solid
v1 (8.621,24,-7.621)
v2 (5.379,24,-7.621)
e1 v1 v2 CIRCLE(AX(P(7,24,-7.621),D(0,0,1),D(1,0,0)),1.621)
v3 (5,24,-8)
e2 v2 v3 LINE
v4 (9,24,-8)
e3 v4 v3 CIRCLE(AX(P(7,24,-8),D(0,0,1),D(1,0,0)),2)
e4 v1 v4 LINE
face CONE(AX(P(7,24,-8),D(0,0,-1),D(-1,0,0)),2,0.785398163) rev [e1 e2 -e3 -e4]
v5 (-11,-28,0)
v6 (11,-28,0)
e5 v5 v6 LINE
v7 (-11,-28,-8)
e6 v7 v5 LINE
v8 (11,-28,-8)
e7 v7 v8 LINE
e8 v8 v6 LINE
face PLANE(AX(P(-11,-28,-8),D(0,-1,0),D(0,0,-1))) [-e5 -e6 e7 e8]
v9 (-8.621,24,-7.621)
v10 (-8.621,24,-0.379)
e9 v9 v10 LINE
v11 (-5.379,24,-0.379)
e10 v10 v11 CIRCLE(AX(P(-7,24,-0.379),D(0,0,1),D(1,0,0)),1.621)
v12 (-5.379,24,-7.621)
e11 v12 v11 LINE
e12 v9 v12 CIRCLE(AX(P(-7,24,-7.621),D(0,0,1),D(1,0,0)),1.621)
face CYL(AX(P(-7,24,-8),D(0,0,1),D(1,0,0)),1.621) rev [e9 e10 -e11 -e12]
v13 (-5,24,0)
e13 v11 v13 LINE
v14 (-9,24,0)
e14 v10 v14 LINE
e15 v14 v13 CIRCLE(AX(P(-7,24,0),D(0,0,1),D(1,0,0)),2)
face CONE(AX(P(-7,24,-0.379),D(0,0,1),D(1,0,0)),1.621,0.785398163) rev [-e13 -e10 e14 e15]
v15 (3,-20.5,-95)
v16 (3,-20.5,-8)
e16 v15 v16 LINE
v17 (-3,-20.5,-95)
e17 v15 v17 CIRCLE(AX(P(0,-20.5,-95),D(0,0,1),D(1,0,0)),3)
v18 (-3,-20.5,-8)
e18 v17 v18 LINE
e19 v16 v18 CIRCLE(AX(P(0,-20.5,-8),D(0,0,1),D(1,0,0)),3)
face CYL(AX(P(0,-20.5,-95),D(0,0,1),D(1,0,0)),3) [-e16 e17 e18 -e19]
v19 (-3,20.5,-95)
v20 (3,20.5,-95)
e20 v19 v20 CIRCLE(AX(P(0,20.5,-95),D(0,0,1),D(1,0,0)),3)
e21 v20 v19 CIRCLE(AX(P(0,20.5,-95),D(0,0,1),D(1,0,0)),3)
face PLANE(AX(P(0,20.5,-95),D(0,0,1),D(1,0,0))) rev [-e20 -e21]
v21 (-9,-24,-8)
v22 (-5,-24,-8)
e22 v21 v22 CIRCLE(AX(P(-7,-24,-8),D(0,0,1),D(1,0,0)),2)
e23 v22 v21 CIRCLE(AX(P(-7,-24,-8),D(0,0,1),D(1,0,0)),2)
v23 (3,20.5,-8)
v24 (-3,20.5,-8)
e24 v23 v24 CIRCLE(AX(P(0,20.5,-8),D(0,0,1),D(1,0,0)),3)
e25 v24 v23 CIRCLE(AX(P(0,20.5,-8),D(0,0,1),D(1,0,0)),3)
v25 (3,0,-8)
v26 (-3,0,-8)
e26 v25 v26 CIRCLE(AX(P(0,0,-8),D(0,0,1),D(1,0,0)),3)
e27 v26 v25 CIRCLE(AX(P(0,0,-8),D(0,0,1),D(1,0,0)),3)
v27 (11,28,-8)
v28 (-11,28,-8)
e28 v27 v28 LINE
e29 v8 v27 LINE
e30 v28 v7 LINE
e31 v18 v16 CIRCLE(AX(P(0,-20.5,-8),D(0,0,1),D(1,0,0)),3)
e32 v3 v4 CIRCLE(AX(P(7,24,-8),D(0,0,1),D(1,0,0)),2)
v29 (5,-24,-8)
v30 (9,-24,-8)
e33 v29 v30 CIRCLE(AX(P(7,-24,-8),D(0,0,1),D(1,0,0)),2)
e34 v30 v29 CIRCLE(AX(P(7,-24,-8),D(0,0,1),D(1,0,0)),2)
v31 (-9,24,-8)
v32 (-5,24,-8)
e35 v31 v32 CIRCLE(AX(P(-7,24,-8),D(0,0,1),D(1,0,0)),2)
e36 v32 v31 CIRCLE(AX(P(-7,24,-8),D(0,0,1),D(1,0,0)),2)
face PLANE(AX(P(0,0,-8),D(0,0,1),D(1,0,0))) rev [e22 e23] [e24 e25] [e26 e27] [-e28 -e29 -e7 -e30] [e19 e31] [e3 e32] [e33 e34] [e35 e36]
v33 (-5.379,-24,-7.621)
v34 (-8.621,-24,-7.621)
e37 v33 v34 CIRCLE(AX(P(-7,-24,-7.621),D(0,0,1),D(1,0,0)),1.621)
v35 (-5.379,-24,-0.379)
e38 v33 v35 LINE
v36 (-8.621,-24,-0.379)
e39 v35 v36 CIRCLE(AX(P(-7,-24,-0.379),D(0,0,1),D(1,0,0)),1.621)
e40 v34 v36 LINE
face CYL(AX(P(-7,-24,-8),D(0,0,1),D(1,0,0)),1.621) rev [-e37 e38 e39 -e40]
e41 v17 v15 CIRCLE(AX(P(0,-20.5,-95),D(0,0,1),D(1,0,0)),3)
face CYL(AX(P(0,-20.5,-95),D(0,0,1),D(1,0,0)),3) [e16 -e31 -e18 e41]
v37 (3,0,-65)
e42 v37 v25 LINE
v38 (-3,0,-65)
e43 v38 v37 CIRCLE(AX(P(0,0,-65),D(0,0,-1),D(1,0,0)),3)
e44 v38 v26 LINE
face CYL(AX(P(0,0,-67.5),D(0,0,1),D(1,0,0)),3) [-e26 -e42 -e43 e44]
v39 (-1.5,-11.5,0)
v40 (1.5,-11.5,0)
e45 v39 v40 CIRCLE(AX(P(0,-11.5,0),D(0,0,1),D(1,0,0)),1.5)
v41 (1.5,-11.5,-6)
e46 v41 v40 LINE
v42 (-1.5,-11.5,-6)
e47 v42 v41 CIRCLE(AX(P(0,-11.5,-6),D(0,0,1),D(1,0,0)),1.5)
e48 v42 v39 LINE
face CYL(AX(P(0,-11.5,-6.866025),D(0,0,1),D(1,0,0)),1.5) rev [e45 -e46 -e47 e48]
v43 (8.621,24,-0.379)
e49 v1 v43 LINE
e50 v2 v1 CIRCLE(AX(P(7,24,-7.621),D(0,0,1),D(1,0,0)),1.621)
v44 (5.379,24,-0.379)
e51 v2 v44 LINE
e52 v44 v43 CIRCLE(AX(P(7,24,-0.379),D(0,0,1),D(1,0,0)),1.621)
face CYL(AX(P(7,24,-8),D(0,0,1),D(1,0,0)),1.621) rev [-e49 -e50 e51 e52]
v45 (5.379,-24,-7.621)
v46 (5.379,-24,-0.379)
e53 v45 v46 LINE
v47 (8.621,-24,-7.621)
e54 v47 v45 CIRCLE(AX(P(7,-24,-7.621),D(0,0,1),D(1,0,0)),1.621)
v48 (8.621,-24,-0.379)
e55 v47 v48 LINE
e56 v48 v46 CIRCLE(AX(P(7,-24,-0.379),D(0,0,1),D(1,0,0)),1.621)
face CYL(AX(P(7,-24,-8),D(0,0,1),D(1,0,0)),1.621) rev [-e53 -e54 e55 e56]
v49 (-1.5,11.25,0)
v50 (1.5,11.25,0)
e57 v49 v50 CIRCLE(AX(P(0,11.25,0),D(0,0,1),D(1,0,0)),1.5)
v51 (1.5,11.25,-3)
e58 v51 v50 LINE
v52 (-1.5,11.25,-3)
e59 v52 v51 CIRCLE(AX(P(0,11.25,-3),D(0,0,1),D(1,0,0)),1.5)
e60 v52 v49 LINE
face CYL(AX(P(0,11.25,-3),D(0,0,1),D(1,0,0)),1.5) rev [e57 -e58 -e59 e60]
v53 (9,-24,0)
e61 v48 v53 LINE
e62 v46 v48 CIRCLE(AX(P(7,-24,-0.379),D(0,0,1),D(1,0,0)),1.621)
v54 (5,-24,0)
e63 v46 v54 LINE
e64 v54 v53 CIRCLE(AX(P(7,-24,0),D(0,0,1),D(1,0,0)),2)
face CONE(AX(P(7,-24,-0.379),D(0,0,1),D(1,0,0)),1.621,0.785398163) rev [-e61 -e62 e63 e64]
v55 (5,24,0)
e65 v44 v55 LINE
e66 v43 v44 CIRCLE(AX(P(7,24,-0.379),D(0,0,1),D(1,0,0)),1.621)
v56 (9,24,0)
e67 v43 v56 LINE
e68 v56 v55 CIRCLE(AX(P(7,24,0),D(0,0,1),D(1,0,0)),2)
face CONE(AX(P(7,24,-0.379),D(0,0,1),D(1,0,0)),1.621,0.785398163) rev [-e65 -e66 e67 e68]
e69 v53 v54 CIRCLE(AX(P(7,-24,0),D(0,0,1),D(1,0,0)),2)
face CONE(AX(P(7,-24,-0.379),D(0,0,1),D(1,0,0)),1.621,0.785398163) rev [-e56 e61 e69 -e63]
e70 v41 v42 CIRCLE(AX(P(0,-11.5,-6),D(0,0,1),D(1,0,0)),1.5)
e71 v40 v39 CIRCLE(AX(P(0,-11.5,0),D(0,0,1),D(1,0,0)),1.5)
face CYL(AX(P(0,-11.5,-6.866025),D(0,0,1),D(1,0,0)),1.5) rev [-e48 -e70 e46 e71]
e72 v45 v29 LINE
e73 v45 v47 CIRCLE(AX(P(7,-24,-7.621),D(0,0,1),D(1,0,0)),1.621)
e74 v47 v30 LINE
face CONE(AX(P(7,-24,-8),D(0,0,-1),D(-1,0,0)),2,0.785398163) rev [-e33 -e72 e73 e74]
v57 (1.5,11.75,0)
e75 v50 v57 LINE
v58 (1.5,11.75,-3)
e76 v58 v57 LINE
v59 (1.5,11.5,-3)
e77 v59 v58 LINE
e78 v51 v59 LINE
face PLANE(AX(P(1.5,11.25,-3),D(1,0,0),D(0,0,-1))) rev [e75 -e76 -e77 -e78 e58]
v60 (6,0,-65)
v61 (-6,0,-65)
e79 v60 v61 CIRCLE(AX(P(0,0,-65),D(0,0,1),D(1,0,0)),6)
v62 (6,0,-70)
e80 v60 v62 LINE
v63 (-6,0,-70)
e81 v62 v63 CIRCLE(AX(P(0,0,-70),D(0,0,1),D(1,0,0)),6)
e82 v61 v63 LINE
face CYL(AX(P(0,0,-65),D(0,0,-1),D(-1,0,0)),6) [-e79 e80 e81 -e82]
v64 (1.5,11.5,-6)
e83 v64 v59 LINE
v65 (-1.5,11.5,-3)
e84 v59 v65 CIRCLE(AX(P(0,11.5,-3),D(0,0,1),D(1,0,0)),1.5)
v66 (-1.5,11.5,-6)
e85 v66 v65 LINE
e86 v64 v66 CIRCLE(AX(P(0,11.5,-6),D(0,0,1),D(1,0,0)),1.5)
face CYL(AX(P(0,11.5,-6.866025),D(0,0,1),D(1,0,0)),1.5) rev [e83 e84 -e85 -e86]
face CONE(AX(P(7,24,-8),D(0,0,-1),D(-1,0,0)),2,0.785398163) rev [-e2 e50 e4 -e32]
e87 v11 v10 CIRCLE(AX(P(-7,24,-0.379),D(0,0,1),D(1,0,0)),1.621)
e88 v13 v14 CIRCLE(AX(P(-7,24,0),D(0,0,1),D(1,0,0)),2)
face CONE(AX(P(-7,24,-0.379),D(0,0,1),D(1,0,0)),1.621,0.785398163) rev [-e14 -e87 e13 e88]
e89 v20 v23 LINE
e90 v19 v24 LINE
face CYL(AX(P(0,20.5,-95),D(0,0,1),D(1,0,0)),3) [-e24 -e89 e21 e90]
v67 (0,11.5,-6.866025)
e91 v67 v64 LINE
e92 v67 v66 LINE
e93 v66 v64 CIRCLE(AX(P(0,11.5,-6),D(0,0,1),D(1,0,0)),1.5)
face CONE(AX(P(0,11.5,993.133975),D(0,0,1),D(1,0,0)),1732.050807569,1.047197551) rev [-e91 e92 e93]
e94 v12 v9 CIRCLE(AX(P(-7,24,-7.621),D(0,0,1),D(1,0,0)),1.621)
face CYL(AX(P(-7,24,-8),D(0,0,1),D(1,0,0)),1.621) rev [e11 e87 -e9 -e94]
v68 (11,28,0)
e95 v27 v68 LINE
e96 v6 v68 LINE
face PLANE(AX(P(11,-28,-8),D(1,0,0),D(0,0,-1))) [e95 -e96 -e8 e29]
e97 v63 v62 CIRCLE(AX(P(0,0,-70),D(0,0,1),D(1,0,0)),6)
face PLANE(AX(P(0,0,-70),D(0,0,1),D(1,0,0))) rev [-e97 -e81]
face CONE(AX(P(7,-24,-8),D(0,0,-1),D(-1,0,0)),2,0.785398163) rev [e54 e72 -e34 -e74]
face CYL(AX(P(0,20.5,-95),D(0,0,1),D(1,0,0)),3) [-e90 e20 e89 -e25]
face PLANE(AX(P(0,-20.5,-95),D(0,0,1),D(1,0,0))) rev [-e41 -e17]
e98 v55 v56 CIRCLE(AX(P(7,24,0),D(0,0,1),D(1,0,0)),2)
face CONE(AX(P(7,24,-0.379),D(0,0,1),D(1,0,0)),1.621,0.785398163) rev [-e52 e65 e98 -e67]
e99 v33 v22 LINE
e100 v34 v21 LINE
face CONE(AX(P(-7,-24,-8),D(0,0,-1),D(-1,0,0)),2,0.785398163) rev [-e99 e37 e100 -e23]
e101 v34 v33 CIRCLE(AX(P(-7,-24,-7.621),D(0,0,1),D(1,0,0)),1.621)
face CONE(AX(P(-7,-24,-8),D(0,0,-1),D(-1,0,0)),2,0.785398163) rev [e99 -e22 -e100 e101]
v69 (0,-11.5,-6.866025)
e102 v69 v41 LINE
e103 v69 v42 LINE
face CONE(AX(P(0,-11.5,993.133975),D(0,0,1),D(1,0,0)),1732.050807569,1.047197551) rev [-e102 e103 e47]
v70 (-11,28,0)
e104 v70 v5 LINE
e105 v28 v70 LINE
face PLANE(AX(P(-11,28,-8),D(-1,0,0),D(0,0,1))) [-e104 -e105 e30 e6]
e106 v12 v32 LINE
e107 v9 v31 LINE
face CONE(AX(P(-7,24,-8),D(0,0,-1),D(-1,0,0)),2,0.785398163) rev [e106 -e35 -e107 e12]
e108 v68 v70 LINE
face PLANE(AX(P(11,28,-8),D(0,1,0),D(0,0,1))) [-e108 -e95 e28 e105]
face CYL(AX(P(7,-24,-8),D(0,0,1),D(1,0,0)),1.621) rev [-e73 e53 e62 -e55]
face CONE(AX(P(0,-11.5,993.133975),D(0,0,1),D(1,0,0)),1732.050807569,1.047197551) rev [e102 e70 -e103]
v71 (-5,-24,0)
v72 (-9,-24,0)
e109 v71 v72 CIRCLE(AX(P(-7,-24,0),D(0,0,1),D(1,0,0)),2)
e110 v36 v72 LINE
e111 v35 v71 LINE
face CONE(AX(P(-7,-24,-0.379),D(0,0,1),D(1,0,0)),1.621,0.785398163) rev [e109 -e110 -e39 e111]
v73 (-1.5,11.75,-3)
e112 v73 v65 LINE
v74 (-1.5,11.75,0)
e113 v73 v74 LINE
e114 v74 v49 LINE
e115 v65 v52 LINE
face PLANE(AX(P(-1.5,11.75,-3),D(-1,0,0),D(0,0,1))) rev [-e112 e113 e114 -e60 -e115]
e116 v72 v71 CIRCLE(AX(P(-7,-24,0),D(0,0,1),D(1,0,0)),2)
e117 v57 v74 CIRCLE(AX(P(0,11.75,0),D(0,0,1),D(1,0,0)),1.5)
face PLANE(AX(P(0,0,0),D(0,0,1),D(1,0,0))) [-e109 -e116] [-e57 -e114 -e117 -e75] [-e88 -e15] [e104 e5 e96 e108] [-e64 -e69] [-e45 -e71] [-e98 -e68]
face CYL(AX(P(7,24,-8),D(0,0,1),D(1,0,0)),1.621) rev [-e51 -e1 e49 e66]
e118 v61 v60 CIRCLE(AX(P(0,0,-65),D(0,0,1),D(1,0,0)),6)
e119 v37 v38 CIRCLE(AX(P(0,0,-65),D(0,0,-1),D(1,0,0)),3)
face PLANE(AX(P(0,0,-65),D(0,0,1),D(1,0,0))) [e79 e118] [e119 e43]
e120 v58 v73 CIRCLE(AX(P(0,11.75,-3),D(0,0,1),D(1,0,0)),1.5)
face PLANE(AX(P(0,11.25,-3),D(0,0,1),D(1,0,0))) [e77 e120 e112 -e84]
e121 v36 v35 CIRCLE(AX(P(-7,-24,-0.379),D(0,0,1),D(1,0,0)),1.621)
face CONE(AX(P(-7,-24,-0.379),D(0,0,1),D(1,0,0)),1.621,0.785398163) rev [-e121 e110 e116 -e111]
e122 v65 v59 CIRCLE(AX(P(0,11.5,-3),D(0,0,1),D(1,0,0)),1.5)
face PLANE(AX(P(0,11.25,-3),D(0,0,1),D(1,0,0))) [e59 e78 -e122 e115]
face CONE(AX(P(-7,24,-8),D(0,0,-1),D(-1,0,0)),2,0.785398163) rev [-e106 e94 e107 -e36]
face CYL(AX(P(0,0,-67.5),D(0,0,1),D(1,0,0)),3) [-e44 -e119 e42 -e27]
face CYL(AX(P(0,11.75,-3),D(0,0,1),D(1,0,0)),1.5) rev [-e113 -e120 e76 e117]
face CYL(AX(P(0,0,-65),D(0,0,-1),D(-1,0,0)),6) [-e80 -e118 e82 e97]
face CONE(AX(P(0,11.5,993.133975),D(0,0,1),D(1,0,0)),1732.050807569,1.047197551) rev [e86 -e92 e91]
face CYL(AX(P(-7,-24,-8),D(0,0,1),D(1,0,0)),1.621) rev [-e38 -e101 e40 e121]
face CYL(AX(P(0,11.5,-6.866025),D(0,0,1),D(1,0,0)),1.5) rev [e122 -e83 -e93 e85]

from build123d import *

# Parameters (mm, degrees)
SKETCH_1_W          = 22
SKETCH_1_H          = 56
EXTRUDE_1_DEPTH     = 8
CUT_EXTRUDE_1_DEPTH = 3
SKETCH_9_R          = 3
EXTRUDE_2_DEPTH     = 87
SKETCH_10_R         = 3
EXTRUDE_3_DEPTH     = 87
SKETCH_11_R         = 3
EXTRUDE_4_DEPTH     = 59.5
SKETCH_12_R         = 6
EXTRUDE_5_DEPTH     = 5


with BuildPart() as part:
    # 草图1 → 凸台-拉伸1 (new body)
    with BuildSketch(Plane.XY):
        Rectangle(SKETCH_1_W, SKETCH_1_H)
    extrude(amount=-EXTRUDE_1_DEPTH)

    # 草图2 → 切除-旋转1 (revolve, cut)
    with BuildSketch(Plane(origin=(0, 24, 0), x_dir=(1, 0, 0), z_dir=(0, 1, 0)), mode=Mode.PRIVATE) as cut_revolve_1_sk:
        Polygon((-7, 0), (-9, 0), (-8.621, 0.379), (-8.621, 7.621), (-9, 8), (-7, 8), align=None)
    revolve(cut_revolve_1_sk.sketch.rotate(Axis((-7, 24, -8), (0, 0, 1)), 180), axis=Axis((-7, 24, -8), (0, 0, 1)), mode=Mode.SUBTRACT)

    # 草图3 → 切除-旋转2 (revolve, cut)
    with BuildSketch(Plane(origin=(0, -24, 0), x_dir=(1, 0, 0), z_dir=(0, 1, 0)), mode=Mode.PRIVATE) as cut_revolve_2_sk:
        Polygon((-7, 0), (-9, 0), (-8.621, 0.379), (-8.621, 7.621), (-9, 8), (-7, 8), align=None)
    revolve(cut_revolve_2_sk.sketch.rotate(Axis((-7, -24, -8), (0, 0, 1)), 180), axis=Axis((-7, -24, -8), (0, 0, 1)), mode=Mode.SUBTRACT)

    # 草图4 → 切除-旋转3 (revolve, cut)
    with BuildSketch(Plane(origin=(0, -24, 0), x_dir=(1, 0, 0), z_dir=(0, 1, 0)), mode=Mode.PRIVATE) as cut_revolve_3_sk:
        Polygon((7, 0), (5, 0), (5.379, 0.379), (5.379, 7.621), (5, 8), (7, 8), align=None)
    revolve(cut_revolve_3_sk.sketch.rotate(Axis((7, -24, -8), (0, 0, 1)), 180), axis=Axis((7, -24, -8), (0, 0, 1)), mode=Mode.SUBTRACT)

    # 草图5 → 切除-旋转4 (revolve, cut)
    with BuildSketch(Plane(origin=(0, 24, 0), x_dir=(1, 0, 0), z_dir=(0, 1, 0)), mode=Mode.PRIVATE) as cut_revolve_4_sk:
        Polygon((7, 0), (5, 0), (5.379, 0.379), (5.379, 7.621), (5, 8), (7, 8), align=None)
    revolve(cut_revolve_4_sk.sketch.rotate(Axis((7, 24, -8), (0, 0, 1)), 180), axis=Axis((7, 24, -8), (0, 0, 1)), mode=Mode.SUBTRACT)

    # 草图6 → 切除-旋转5 (revolve, cut)
    with BuildSketch(Plane(origin=(0, 0, 0), x_dir=(0, 0, -1), z_dir=(1, 0, 0)), mode=Mode.PRIVATE) as cut_revolve_5_sk:
        Polygon((0, 11.5), (0, 13), (6, 13), (6.866025404, 11.5), align=None)
    revolve(cut_revolve_5_sk.sketch.rotate(Axis((0, 11.5, -6.866025404), (0, 0, 1)), 270), axis=Axis((0, 11.5, -6.866025404), (0, 0, 1)), mode=Mode.SUBTRACT)

    # 草图7 → 切除-旋转6 (revolve, cut)
    with BuildSketch(Plane(origin=(0, 0, 0), x_dir=(0, 0, -1), z_dir=(1, 0, 0)), mode=Mode.PRIVATE) as cut_revolve_6_sk:
        Polygon((0, -11.5), (0, -10), (6, -10), (6.866025404, -11.5), align=None)
    revolve(cut_revolve_6_sk.sketch.rotate(Axis((0, -11.5, -6.866025404), (0, 0, 1)), 270), axis=Axis((0, -11.5, -6.866025404), (0, 0, 1)), mode=Mode.SUBTRACT)

    # 草图8 → 切除-拉伸1 (cut)
    with BuildSketch(Plane.XY):
        with BuildLine():
            Line((1.5, 11.25), (1.5, 11.75))
            ThreePointArc((1.5, 11.75), (0, 13.25), (-1.5, 11.75))
            Line((-1.5, 11.75), (-1.5, 11.25))
            ThreePointArc((-1.5, 11.25), (0, 9.75), (1.5, 11.25))
        make_face()
    extrude(amount=-CUT_EXTRUDE_1_DEPTH, mode=Mode.SUBTRACT)

    # 草图9 → 凸台-拉伸2 (add)
    with BuildSketch(Plane.XY.offset(-8)):
        with Locations((0, 20.5)):
            Circle(SKETCH_9_R)
    extrude(amount=-EXTRUDE_2_DEPTH)

    # 草图10 → 凸台-拉伸3 (add)
    with BuildSketch(Plane.XY.offset(-8)):
        with Locations((0, -20.5)):
            Circle(SKETCH_10_R)
    extrude(amount=-EXTRUDE_3_DEPTH)

    # 草图11 → 凸台-拉伸4 (add)
    with BuildSketch(Plane.XY.offset(-8)):
        Circle(SKETCH_11_R)
    extrude(amount=-EXTRUDE_4_DEPTH)

    # 草图12 → 凸台-拉伸5 (add)
    with BuildSketch(Plane.XY.offset(-70)):
        Circle(SKETCH_12_R)
    extrude(amount=EXTRUDE_5_DEPTH)


solid = part.part
